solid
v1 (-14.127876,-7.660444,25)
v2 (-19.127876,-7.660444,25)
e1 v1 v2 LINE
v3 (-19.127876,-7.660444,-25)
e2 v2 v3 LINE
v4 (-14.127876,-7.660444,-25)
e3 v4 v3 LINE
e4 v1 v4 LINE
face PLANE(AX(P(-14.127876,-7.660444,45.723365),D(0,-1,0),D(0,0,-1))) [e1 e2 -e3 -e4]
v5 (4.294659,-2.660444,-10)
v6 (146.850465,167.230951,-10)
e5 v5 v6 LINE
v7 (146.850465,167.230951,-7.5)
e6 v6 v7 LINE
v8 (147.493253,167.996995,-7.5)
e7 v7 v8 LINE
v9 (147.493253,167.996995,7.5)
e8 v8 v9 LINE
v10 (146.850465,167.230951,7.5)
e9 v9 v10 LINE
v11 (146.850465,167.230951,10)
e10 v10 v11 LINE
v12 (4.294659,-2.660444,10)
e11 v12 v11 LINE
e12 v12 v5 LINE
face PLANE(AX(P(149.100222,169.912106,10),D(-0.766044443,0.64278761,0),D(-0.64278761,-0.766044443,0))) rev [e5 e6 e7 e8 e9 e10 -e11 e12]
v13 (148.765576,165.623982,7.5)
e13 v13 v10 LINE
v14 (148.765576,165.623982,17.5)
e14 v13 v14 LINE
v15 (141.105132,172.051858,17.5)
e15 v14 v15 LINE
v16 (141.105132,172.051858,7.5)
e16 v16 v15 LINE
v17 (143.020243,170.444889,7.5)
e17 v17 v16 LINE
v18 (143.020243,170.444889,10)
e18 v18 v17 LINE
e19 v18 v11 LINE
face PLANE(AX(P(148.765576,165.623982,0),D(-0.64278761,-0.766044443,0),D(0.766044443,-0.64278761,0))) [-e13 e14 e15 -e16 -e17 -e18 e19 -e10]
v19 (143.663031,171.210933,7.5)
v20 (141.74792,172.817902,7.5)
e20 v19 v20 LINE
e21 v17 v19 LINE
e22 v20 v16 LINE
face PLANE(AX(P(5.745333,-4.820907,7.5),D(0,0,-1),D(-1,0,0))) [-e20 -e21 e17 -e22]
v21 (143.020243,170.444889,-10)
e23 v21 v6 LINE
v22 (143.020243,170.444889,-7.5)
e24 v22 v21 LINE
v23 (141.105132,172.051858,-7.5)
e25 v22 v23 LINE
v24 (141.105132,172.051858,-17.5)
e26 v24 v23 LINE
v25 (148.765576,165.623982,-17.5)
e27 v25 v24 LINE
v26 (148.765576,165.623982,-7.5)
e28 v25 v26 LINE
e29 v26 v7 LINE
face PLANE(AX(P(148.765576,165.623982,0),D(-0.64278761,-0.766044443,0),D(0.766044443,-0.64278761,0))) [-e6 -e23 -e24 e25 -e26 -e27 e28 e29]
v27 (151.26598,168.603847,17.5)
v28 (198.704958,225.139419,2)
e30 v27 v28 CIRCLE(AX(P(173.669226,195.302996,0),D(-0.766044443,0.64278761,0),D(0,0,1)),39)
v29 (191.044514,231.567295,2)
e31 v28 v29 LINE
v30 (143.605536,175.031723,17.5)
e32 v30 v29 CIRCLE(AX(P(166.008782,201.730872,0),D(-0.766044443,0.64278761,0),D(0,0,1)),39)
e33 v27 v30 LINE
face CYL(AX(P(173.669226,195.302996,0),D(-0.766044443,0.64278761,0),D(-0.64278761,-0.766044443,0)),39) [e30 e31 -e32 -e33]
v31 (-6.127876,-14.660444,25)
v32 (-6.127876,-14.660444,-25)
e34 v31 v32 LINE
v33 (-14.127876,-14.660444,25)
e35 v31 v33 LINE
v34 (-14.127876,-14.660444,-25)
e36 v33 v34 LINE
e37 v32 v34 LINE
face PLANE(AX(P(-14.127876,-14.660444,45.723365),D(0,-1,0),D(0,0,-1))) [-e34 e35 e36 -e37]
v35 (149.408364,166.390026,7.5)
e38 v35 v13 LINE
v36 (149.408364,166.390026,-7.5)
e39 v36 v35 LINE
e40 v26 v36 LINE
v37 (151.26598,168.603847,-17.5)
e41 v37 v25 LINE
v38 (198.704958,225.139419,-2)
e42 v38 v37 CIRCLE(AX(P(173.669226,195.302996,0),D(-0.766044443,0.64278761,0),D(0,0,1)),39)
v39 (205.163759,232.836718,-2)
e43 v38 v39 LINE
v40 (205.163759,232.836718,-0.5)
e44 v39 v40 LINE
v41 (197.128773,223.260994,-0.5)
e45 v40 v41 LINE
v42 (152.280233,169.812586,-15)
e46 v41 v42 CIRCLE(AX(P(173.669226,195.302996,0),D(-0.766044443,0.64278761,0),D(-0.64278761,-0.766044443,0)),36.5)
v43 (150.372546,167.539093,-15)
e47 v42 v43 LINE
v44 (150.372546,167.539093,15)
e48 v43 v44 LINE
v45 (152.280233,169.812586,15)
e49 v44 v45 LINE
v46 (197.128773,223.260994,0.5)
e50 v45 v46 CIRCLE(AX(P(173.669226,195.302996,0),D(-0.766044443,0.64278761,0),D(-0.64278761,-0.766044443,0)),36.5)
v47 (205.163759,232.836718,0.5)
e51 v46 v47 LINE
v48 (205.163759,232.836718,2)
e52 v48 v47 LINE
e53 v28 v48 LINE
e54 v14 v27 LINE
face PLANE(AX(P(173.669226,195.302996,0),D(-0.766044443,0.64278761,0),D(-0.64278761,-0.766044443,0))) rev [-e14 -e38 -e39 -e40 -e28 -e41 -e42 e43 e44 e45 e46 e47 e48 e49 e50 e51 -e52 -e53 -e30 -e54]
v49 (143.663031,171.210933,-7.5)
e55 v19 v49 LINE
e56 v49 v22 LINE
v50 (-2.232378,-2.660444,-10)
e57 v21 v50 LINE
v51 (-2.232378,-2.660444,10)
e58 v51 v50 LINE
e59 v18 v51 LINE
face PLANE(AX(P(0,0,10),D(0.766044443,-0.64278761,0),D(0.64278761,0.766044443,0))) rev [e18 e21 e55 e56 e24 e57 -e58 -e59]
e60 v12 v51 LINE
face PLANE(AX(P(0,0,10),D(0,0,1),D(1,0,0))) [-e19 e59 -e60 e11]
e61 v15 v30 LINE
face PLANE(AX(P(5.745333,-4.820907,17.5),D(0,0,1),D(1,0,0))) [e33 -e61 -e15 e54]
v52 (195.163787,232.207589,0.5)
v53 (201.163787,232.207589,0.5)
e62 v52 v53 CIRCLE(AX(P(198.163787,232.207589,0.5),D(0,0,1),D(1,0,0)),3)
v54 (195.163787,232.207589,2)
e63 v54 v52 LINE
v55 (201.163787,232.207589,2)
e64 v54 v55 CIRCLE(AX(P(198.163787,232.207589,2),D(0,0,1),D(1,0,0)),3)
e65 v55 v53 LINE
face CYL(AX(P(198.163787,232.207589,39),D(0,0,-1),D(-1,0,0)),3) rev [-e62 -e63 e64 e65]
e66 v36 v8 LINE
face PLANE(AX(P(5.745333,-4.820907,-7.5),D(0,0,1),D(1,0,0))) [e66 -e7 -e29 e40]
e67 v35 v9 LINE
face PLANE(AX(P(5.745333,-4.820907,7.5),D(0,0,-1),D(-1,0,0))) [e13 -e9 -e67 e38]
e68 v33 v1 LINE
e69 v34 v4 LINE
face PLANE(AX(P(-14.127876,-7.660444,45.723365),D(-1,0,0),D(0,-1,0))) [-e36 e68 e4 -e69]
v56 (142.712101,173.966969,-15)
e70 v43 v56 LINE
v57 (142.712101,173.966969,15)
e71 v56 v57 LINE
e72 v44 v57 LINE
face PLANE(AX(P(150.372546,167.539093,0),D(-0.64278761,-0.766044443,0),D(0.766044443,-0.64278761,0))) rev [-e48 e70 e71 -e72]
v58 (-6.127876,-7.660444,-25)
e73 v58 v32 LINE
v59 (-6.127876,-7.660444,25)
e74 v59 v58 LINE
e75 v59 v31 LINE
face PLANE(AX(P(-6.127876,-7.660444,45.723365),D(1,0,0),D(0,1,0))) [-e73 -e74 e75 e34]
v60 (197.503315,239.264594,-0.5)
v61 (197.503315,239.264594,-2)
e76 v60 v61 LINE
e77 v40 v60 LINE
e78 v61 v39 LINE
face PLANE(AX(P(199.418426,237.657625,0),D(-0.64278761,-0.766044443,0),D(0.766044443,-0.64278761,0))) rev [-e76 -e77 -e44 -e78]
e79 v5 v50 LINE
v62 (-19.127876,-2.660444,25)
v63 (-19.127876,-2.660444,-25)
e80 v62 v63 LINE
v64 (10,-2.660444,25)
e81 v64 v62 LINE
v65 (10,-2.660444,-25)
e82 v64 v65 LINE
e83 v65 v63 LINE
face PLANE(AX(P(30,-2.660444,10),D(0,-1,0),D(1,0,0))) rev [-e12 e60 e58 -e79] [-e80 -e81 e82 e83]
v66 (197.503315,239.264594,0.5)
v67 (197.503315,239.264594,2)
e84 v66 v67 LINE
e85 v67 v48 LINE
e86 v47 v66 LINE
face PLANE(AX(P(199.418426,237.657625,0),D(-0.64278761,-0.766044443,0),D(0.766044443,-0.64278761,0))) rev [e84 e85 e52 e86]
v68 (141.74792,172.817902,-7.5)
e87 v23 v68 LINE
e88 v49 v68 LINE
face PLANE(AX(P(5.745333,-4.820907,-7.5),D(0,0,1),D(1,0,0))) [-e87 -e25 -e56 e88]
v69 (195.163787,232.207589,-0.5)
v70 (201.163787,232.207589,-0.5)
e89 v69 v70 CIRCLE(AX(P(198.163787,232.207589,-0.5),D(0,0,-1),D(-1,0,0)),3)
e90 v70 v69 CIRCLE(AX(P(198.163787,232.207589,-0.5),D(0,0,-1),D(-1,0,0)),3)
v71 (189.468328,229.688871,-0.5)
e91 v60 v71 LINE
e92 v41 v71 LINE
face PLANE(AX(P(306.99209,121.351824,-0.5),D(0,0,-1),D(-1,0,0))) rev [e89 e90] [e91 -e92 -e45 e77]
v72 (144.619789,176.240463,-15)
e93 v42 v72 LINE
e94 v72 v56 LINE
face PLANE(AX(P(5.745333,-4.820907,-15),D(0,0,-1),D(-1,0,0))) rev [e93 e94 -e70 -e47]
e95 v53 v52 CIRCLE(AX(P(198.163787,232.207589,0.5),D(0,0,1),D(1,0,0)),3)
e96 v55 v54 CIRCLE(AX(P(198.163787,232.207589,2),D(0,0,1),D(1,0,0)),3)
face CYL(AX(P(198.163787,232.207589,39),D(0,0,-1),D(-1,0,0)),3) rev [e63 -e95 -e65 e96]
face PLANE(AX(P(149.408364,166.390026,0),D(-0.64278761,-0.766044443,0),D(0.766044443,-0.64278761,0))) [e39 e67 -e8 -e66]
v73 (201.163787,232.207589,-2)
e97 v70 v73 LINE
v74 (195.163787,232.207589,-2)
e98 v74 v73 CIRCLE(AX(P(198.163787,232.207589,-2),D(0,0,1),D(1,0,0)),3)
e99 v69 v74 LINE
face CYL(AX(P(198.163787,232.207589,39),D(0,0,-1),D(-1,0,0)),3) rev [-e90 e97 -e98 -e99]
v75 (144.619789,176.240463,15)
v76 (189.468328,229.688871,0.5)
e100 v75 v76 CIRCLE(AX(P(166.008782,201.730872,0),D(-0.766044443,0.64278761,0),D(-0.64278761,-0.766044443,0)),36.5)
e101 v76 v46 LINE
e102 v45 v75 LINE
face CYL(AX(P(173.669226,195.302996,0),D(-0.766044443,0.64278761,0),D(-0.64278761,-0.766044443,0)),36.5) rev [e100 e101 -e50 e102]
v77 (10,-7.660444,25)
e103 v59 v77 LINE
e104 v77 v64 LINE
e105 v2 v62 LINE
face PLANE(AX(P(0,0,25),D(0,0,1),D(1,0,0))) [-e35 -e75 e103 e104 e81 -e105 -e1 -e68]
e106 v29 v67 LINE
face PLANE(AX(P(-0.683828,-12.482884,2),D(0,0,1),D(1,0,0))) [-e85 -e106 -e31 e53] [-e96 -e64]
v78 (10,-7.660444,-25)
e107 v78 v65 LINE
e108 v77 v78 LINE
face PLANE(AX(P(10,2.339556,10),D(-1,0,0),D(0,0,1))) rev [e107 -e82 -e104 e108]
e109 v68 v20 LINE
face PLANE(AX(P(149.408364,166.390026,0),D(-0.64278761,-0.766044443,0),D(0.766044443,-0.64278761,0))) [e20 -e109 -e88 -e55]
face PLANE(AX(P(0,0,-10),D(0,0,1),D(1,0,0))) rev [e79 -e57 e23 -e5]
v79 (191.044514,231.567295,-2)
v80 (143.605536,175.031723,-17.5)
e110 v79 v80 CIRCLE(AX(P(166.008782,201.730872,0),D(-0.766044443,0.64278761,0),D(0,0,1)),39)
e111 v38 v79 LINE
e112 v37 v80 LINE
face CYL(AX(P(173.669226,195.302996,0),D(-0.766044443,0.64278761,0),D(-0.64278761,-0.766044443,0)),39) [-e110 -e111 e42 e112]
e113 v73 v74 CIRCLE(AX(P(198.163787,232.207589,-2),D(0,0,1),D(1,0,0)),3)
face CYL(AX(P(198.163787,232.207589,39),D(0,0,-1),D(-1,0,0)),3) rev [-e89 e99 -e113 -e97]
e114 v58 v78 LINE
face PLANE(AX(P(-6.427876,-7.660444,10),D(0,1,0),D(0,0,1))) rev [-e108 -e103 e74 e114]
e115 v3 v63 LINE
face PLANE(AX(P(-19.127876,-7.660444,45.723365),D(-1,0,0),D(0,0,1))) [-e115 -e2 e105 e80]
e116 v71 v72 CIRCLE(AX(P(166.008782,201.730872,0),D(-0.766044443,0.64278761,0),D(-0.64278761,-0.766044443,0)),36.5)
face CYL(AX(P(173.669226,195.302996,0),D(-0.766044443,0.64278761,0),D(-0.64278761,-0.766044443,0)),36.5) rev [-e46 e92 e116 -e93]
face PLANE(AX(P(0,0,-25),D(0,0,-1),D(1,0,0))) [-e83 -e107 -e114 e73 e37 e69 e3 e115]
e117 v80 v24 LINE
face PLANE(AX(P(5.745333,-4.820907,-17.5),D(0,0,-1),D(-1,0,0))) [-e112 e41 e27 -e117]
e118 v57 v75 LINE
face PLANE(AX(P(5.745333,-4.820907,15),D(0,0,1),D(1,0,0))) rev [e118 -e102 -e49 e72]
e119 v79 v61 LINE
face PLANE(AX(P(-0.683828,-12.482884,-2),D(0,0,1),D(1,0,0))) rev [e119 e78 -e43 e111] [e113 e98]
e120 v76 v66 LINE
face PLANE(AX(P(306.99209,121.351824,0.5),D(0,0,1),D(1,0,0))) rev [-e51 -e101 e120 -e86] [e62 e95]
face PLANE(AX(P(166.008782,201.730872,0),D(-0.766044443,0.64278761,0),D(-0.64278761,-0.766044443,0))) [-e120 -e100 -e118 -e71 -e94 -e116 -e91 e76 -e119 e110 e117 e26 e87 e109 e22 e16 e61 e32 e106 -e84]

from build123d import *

# Parameters (mm, degrees)
EXTRUDE_1_DEPTH               = 10
EXTRUDE_2_DEPTH               = 5
EXTRUDE_2_DEPTH_BACK          = 5
EXTRUDE_2_START               = -2.5
CUT_EXTRUDE_3_DEPTH           = 308.667661103
CUT_EXTRUDE_3_DEPTH_BACK      = 308.667661103
SKETCH_4_W                    = 20
SKETCH_4_H                    = 2.700809371
CUT_EXTRUDE_2_DEPTH           = 308.667661103
CUT_EXTRUDE_2_DEPTH_BACK      = 308.667661103
SKETCH_5_W                    = 1
SKETCH_5_H                    = 14.903200109
SKETCH_8_W                    = 10
SKETCH_8_H                    = 1.5
EXTRUDE_2_2_DEPTH             = 10
EXTRUDE_2_2_DIRECTION_2_REACH = 314.682
SKETCH_11_W                   = 20
SKETCH_11_H                   = 26.003490823
CUT_EXTRUDE_4_DEPTH           = 10
EXTRUDE_3_DEPTH               = 15
CUT_EXTRUDE_5_DEPTH           = 318.837559332
CUT_EXTRUDE_5_DEPTH_BACK      = 318.837559332
SKETCH_13_R                   = 3
EXTRUDE_4_DEPTH               = 50


with BuildPart() as part:
    # 草图1 → 凸台-拉伸1 (new, symmetric)
    with BuildSketch(Plane.XY):
        Polygon((0, 0), (138.199336083, 164.699555271), (145.269999789, 173.126044145), (149.100222005, 169.912106096), (142.029558298, 161.485617222), (10.722534603, 5), (4.294658506, -2.660444431), (30, -2.660444431), (30, -7.660444431), (-6.427876097, -7.660444431), align=None)
    extrude(amount=EXTRUDE_1_DEPTH, both=True)

    # 草图3 → Extrude 2 (add, two sides: drawn at the far end of the back side and taken through both)
    with BuildSketch(Plane(origin=(0, 0, 0), x_dir=(0, 0, 1), z_dir=(-0.766044443118979, 0.642787609686538, 0)).offset(EXTRUDE_2_START - EXTRUDE_2_DEPTH_BACK)):
        with BuildLine():
            Line((-17.5, 226.389937847), (-17.5, 226.243201682))
            Line((-17.5, 226.243201682), (-17.5, 222.5))
            Line((-17.5, 222.5), (-7.5, 222.5))
            Line((-7.5, 222.5), (-7.5, 223.5))
            Line((-7.5, 223.5), (7.5, 223.5))
            Line((7.5, 223.5), (7.5, 222.5))
            Line((7.5, 222.5), (17.5, 222.5))
            Line((17.5, 222.5), (17.5, 226.243201682))
            Line((17.5, 226.243201682), (17.5, 226.389937847))
            ThreePointArc((17.5, 226.389937847), (0, 300.243201682), (-17.5, 226.389937847))
        make_face()
        with BuildLine():
            Line((-15, 227.967835418), (-15, 226.243201682))
            Line((-15, 226.243201682), (-15, 225))
            Line((-15, 225), (-10, 225))
            Line((-10, 225), (-10, 226))
            Line((-10, 226), (10, 226))
            Line((10, 226), (10, 225))
            Line((10, 225), (15, 225))
            Line((15, 225), (15, 226.243201682))
            Line((15, 226.243201682), (15, 227.967835418))
            ThreePointArc((15, 227.967835418), (0, 297.743201682), (-15, 227.967835418))
        make_face(mode=Mode.SUBTRACT)
    extrude(amount=EXTRUDE_2_DEPTH + EXTRUDE_2_DEPTH_BACK)

    # 草图4 → 切除-拉伸3 (cut, two sides: drawn at the far end of the back side and taken through both)
    with BuildSketch(Plane(origin=(0, 0, 0), x_dir=(0, 0, 1), z_dir=(-0.7660444431189785, 0.6427876096865388, 0)).offset(-CUT_EXTRUDE_3_DEPTH_BACK)):
        with Locations((0, 226.350404685)):
            Rectangle(SKETCH_4_W, SKETCH_4_H)
    extrude(amount=CUT_EXTRUDE_3_DEPTH + CUT_EXTRUDE_3_DEPTH_BACK, mode=Mode.SUBTRACT)

    # 草图5 → 切除-拉伸2 (cut, two sides: drawn at the far end of the back side and taken through both)
    with BuildSketch(Plane(origin=(0, 0, 0), x_dir=(0, 0, 1), z_dir=(-0.7660444431189785, 0.6427876096865388, 0)).offset(-CUT_EXTRUDE_2_DEPTH_BACK)):
        with Locations((0, 297.743201683)):
            Rectangle(SKETCH_5_W, SKETCH_5_H)
    extrude(amount=CUT_EXTRUDE_2_DEPTH + CUT_EXTRUDE_2_DEPTH_BACK, mode=Mode.SUBTRACT)

    # 草图8 → Extrude 2 2 (add)
    with BuildSketch(Plane(origin=(192.990549633, 229.997180861, 0), x_dir=(0.766044443118979, -0.6427876096865381, 0), z_dir=(0.6427876096865381, 0.766044443118979, 0))):
        with Locations((2.5, -1.25)):
            Rectangle(SKETCH_8_W, SKETCH_8_H)
    extrude_2_2 = extrude(amount=EXTRUDE_2_2_DEPTH)

    # 草图8 → Extrude 2 2 direction 2 (add, up to next)
    with BuildSketch(Plane(origin=(192.990549633, 229.997180861, 0), x_dir=(0.766044443118979, -0.6427876096865381, 0), z_dir=(0.6427876096865381, 0.766044443118979, 0)), mode=Mode.PRIVATE) as extrude_2_2_direction_2_sk1:
        with Locations((2.5, -1.25)):
            Rectangle(SKETCH_8_W, SKETCH_8_H)
    extrude_2_2_direction_2_tool1 = extrude(extrude_2_2_direction_2_sk1.sketch, amount=-EXTRUDE_2_2_DIRECTION_2_REACH, mode=Mode.PRIVATE) - part.part
    extrude_2_2_direction_2 = extrude_2_2_direction_2_tool1.solids().sort_by_distance((194.905661, 228.390212, 1.25))[0]
    add(extrude_2_2_direction_2)

    # 镜向1: Extrude 2 2, Extrude 2 2 direction 2 across plane
    add(extrude_2_2.mirror(Plane.XY))
    add(extrude_2_2_direction_2.mirror(Plane.XY))

    # 草图11 → 切除-拉伸4 (cut)
    with BuildSketch(Plane.XZ.offset(7.660444431)):
        with Locations((20, -3.001745411)):
            Rectangle(SKETCH_11_W, SKETCH_11_H)
    extrude(amount=-CUT_EXTRUDE_4_DEPTH, mode=Mode.SUBTRACT)

    # 草图12 → 凸台-拉伸3 (add)
    with BuildSketch(Plane.XY.offset(10)):
        Polygon((4.294658506, -2.660444431), (-2.232377941, -2.660444431), (-6.427876097, -7.660444431), (10, -7.660444431), (10, -2.660444431), align=None)
    extrude_3 = extrude(amount=EXTRUDE_3_DEPTH)

    # 镜向2: 凸台-拉伸3 across plane
    add(extrude_3.mirror(Plane.XY))

    # 草图13 → 切除-拉伸5 (cut, two sides: drawn at the far end of the back side and taken through both)
    with BuildSketch(Plane(origin=(0, 0, -2), x_dir=(-1, 0, 0), z_dir=(0, 0, -1)).offset(-CUT_EXTRUDE_5_DEPTH_BACK)):
        with Locations((-198.163787282, 232.207589437)):
            Circle(SKETCH_13_R)
    extrude(amount=CUT_EXTRUDE_5_DEPTH + CUT_EXTRUDE_5_DEPTH_BACK, mode=Mode.SUBTRACT)

    # 草图14 → 凸台-拉伸4 (add)
    with BuildSketch(Plane(origin=(0, 0, -25), x_dir=(-1, 0, 0), z_dir=(0, 0, -1))):
        Polygon((2.232377941, -2.660444431), (6.427876097, -2.660444431), (14.127876097, -2.660444431), (19.127876097, -2.660444431), (19.127876097, -7.660444431), (14.127876097, -7.660444431), (14.127876097, -14.660444431), (6.427876097, -14.660444431), (6.127876097, -14.660444431), (6.127876097, -7.660444431), (6.427876097, -7.660444431), align=None)
    extrude(amount=-EXTRUDE_4_DEPTH)


solid = part.part
